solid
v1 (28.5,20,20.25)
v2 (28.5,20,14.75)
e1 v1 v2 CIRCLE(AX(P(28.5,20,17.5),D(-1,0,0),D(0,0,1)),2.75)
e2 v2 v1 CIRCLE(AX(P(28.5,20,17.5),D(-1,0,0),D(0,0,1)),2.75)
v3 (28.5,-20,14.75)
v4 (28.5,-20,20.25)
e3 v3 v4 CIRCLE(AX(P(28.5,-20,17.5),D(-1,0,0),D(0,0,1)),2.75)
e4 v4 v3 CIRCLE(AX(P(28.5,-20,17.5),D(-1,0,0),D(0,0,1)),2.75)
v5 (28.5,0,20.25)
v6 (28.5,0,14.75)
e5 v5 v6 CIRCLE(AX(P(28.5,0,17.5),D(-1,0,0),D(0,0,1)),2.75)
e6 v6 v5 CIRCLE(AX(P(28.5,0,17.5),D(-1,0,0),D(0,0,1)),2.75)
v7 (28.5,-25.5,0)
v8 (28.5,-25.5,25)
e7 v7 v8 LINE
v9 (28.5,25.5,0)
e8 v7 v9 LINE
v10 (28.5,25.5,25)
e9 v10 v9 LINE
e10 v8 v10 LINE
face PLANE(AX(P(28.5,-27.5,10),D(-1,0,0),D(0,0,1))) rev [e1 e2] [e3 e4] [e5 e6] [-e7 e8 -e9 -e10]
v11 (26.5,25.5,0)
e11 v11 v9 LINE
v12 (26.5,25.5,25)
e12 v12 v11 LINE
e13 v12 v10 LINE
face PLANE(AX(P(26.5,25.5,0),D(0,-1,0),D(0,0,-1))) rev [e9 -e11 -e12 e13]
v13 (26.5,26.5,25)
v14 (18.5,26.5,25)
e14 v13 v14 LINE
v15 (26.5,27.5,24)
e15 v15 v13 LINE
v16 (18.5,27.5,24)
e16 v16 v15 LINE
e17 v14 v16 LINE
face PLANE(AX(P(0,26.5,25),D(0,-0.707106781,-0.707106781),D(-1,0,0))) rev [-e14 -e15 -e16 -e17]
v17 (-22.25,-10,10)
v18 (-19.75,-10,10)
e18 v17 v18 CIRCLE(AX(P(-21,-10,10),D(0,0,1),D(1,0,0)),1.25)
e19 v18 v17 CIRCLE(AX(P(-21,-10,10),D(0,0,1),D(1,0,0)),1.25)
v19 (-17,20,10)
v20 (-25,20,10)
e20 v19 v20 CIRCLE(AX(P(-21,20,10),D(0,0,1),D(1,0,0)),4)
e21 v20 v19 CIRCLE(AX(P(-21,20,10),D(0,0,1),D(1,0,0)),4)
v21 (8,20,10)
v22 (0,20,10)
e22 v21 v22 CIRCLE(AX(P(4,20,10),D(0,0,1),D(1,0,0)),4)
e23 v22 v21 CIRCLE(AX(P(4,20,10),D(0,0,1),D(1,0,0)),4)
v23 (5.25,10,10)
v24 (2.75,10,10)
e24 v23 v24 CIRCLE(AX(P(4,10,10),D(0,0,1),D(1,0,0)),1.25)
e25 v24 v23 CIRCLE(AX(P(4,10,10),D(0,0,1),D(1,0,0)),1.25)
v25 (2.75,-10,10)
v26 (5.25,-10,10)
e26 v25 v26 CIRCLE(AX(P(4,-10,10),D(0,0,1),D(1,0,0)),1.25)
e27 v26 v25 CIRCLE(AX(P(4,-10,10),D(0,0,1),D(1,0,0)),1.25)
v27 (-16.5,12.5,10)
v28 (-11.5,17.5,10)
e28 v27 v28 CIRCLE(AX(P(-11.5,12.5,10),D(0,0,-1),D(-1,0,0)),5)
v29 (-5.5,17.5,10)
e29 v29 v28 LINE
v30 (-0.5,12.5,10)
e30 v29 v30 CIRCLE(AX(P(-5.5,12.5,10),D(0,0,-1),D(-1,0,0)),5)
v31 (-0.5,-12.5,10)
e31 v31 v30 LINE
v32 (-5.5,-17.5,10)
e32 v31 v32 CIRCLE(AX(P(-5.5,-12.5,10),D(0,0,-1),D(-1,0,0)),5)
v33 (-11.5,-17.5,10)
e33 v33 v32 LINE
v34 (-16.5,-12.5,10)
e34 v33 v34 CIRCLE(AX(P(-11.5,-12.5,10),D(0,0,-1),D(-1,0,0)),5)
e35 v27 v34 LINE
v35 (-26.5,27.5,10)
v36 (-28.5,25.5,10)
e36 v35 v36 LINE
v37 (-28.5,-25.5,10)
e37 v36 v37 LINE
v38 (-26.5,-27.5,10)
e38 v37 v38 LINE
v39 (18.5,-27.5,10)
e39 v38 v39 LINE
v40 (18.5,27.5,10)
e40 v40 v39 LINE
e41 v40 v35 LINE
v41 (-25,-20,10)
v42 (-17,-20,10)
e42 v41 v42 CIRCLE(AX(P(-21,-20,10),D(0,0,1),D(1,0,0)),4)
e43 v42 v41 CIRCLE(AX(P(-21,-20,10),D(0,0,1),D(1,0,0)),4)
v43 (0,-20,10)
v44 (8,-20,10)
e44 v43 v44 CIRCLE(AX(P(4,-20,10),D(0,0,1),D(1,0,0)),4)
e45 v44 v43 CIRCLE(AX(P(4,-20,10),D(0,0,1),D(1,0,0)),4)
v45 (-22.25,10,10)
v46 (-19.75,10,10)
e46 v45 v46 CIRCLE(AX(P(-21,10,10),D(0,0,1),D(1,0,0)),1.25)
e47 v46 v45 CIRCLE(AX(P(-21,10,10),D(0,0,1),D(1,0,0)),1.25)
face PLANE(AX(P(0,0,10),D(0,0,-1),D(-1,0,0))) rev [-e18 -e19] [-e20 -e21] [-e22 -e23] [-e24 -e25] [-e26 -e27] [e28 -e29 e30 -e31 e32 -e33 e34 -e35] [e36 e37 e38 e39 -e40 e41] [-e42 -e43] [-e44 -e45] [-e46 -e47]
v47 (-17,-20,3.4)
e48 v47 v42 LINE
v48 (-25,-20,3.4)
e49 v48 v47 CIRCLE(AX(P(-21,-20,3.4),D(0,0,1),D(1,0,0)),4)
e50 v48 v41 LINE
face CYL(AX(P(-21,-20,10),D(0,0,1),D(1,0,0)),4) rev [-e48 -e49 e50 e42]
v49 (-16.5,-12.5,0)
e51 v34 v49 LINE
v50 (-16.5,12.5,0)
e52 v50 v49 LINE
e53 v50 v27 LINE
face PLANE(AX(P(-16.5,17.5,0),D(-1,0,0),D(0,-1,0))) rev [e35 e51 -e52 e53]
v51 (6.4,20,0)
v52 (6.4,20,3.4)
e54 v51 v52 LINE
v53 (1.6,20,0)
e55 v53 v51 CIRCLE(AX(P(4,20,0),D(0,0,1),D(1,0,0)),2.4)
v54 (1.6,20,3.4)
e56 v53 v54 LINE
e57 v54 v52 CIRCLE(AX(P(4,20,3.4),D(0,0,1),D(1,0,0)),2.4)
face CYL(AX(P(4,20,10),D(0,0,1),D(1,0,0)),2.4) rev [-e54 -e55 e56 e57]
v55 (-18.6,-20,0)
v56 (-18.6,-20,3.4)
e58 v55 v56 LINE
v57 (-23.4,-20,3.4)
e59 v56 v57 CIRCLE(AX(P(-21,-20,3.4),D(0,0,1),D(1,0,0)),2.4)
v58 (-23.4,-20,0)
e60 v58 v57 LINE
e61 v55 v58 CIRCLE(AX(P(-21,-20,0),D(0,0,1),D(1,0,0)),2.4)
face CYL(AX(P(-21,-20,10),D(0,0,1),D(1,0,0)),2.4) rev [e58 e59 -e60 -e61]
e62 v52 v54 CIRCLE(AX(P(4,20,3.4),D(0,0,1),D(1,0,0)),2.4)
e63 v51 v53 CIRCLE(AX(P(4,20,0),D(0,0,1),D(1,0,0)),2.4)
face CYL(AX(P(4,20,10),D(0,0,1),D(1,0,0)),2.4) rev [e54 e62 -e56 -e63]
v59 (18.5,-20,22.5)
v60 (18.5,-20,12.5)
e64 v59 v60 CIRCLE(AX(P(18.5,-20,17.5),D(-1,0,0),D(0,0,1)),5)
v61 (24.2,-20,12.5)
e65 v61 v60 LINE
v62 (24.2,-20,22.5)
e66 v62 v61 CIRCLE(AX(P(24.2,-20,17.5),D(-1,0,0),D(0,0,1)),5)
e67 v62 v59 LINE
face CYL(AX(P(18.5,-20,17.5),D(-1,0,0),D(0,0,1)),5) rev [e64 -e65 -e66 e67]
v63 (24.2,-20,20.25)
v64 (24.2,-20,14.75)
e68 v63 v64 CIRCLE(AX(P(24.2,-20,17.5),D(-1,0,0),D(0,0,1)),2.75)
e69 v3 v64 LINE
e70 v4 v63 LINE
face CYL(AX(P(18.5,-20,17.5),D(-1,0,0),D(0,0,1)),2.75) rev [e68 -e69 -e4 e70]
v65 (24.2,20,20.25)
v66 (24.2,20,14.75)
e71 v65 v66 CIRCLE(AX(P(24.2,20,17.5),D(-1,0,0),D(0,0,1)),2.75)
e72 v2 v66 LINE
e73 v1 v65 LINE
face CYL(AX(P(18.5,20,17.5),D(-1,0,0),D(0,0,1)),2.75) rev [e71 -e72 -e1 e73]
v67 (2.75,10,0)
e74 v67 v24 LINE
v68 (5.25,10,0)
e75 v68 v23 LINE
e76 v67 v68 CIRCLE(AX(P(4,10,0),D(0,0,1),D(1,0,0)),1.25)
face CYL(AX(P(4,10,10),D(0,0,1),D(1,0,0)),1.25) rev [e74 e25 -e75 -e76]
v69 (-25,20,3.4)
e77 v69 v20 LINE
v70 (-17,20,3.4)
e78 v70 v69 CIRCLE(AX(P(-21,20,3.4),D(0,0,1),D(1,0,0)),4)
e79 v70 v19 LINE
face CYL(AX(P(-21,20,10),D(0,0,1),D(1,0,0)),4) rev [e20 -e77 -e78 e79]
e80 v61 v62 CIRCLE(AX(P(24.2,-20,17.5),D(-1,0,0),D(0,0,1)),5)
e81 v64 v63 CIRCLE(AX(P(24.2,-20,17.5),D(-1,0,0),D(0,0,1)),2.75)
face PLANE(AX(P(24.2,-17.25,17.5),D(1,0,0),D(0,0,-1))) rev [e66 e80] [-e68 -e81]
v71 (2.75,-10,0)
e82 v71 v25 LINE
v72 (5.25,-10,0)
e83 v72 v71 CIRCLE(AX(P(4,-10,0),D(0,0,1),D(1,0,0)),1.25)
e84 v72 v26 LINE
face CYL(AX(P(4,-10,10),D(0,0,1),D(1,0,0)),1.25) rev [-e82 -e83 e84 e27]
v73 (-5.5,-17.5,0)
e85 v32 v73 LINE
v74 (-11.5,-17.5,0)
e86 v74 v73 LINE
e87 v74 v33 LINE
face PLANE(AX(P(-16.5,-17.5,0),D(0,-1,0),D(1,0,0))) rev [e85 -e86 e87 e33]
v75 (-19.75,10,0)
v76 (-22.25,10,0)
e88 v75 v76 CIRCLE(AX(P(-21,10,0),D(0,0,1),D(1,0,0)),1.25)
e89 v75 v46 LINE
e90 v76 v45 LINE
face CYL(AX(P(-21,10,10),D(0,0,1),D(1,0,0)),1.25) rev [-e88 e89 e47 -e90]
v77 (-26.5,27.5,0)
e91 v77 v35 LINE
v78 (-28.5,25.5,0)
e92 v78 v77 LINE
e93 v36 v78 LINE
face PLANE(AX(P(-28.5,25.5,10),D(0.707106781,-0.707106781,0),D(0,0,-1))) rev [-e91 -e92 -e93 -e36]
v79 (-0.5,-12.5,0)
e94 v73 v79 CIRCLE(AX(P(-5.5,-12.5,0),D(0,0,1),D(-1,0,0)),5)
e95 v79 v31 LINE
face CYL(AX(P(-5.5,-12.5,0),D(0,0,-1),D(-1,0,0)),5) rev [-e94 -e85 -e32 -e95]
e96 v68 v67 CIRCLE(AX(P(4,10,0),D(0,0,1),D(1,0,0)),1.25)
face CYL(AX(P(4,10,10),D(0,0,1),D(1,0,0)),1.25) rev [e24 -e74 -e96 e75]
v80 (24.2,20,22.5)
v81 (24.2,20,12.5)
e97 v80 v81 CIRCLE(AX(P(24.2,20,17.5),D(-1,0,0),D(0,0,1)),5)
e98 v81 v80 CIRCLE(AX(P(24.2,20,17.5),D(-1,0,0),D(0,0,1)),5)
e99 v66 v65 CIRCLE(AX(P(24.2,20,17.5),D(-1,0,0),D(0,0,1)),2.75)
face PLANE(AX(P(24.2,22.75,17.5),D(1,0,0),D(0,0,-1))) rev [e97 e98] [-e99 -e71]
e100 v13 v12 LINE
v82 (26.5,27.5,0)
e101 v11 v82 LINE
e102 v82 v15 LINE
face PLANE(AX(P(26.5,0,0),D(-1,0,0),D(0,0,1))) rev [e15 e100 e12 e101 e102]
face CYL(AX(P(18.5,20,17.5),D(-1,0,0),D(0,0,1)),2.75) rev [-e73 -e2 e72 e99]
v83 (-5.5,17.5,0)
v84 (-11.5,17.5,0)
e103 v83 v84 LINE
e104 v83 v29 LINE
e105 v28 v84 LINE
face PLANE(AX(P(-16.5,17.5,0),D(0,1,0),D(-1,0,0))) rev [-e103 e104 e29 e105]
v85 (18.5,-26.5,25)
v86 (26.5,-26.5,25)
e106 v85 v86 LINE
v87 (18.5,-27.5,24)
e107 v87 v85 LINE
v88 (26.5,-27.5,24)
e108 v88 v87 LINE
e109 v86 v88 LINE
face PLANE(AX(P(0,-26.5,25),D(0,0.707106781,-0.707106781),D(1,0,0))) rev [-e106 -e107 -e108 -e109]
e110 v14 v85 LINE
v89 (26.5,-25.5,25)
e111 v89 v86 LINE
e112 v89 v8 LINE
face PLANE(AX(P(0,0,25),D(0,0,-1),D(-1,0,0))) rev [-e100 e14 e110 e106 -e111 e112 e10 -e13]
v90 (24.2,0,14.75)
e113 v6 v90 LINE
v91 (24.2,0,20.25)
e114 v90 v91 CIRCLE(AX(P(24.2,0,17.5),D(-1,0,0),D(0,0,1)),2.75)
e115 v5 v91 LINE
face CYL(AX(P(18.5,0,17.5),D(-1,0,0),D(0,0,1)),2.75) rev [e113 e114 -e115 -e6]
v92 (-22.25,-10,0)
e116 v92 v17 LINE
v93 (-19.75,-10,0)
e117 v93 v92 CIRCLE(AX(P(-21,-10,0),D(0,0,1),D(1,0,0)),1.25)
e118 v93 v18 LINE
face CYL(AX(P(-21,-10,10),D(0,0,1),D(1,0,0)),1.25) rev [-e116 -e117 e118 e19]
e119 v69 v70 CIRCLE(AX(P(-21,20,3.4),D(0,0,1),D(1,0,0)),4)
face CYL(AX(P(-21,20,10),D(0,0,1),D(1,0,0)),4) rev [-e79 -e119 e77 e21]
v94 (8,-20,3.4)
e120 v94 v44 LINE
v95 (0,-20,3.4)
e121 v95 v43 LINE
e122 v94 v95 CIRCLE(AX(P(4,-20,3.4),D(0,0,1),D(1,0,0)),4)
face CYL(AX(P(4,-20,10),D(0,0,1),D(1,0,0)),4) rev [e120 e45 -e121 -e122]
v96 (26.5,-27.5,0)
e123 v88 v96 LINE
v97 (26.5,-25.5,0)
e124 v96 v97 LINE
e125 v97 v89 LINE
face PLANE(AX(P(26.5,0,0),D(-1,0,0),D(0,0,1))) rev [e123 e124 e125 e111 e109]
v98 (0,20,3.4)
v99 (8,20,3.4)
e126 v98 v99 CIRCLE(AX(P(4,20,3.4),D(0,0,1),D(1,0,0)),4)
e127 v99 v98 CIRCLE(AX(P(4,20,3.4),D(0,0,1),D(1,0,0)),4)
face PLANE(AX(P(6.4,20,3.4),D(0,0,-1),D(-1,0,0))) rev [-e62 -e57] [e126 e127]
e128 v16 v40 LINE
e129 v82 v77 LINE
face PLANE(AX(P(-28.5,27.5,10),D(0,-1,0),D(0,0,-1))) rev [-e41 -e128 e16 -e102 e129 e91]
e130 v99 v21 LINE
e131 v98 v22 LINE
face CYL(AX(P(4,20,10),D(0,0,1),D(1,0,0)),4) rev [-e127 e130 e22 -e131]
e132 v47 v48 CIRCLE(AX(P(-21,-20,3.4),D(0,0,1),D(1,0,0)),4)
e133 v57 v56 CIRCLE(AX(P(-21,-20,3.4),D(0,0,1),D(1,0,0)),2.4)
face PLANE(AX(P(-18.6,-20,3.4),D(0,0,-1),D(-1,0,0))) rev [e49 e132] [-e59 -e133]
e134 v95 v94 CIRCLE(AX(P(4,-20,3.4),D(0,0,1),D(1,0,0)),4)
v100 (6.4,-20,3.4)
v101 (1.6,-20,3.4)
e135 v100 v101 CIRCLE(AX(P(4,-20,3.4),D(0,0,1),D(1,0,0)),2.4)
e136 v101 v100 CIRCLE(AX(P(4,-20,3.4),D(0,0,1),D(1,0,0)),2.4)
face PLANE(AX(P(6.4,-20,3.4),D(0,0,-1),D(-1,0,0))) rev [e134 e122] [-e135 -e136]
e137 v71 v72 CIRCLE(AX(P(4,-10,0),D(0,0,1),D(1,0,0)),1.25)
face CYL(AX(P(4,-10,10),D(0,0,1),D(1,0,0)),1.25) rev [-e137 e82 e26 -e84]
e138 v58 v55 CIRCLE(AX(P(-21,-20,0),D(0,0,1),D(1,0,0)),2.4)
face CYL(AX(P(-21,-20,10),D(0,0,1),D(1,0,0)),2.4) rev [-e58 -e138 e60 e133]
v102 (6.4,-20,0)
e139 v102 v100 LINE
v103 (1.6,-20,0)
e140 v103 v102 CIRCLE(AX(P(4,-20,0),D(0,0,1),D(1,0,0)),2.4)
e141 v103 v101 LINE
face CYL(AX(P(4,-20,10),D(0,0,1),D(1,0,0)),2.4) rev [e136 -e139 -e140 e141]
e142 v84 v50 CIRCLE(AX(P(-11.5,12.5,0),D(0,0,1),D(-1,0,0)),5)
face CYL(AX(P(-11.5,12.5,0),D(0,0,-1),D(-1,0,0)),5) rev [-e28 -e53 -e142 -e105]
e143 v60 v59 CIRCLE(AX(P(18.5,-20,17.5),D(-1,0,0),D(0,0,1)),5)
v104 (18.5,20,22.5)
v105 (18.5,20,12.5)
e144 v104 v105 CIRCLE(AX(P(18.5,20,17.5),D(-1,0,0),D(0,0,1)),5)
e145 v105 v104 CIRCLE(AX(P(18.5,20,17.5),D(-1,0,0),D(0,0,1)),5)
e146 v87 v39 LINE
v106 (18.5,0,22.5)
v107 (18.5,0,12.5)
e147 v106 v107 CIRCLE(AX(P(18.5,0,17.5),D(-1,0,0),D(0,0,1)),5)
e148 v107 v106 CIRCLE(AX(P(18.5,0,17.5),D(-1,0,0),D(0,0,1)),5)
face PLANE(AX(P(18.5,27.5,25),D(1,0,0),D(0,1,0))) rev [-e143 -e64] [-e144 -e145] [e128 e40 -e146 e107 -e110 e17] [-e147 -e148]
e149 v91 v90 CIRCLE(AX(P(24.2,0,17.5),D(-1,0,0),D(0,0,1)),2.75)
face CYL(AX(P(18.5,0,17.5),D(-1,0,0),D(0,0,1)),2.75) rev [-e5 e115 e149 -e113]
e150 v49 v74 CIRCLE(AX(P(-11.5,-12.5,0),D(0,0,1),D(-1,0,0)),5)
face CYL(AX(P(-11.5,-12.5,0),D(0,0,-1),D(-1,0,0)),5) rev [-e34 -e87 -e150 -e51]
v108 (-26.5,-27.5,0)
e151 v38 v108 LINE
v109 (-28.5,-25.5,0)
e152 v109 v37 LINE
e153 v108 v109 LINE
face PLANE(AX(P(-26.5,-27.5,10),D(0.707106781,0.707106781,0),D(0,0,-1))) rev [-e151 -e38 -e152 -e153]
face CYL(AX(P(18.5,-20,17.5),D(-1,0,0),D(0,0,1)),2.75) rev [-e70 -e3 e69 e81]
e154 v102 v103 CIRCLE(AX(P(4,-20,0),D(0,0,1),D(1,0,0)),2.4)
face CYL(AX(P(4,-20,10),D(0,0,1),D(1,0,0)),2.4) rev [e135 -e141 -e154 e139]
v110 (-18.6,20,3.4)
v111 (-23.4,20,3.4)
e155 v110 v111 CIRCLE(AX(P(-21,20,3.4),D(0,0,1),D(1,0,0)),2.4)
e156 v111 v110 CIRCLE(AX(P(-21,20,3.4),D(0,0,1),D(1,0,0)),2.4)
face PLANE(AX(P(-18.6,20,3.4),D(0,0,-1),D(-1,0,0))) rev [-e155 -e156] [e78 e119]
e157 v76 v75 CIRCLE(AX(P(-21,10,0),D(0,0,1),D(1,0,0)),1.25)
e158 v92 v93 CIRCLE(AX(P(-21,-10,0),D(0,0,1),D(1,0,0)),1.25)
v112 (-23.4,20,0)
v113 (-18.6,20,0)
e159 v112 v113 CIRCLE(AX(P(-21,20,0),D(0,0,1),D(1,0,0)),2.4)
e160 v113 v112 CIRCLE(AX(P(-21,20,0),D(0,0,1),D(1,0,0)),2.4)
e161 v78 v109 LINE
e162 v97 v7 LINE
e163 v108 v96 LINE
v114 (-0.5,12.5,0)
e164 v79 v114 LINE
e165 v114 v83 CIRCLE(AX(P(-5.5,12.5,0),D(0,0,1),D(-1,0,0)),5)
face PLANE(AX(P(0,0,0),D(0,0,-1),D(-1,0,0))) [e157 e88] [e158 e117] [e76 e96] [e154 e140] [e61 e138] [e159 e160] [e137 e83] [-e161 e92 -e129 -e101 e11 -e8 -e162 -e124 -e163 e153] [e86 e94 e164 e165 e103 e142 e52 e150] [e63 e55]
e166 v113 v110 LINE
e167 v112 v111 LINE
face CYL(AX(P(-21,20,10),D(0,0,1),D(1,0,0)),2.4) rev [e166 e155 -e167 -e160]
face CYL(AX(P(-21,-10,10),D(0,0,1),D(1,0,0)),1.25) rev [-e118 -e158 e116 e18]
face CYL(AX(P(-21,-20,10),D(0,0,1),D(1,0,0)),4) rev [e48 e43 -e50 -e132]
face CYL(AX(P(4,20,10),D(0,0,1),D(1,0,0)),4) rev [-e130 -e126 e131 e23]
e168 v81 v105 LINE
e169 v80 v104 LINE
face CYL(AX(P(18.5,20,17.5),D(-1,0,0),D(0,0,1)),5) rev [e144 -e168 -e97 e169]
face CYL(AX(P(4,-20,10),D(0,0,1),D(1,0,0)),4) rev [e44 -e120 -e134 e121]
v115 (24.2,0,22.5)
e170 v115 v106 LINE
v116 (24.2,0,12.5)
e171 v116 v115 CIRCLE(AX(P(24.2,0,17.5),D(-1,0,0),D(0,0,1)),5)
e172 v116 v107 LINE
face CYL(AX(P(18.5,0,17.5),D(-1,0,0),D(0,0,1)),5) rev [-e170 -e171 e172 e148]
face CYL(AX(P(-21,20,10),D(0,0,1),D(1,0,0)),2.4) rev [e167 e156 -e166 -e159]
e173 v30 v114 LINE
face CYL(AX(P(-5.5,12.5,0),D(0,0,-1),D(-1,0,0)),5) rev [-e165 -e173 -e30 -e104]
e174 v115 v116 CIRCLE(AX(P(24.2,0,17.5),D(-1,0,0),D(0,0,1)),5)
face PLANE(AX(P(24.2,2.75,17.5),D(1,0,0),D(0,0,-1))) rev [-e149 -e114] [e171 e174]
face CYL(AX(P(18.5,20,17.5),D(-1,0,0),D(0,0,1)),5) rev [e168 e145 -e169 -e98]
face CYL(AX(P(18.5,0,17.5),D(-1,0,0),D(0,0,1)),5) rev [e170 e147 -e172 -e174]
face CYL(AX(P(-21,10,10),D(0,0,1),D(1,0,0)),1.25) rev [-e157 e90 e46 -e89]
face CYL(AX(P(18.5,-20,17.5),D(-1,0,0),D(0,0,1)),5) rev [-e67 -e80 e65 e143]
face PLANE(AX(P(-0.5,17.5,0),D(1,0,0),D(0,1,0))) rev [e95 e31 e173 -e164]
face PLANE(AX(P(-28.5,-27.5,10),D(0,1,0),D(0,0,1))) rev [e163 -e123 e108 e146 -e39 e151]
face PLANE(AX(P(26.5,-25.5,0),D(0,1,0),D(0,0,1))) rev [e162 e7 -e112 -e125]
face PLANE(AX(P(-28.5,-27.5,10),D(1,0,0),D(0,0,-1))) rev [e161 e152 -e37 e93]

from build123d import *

# Parameters (mm, degrees)
SKETCH_1_W                = 57
SKETCH_1_H                = 55
EXTRUDE_1_DEPTH           = 10
SKETCH_2_W                = 16
SKETCH_2_H                = 35
CUT_EXTRUDE_1_DEPTH       = 41.847276531
HOLE_WIZARD_1_D           = 4.8
HOLE_WIZARD_1_CBORE_D     = 8
HOLE_WIZARD_1_CBORE_DEPTH = 6.6
HOLE_WIZARD_M3_1_D        = 2.5
FILLET_1_R                = 5
SKETCH_8_W                = 10
SKETCH_8_H                = 55
EXTRUDE_2_DEPTH           = 15
HOLE_WIZARD_2_D           = 5.5
HOLE_WIZARD_2_CBORE_D     = 10
HOLE_WIZARD_2_CBORE_DEPTH = 5.7
SKETCH_11_W               = 25
SKETCH_11_H               = 2
CUT_EXTRUDE_2_DEPTH       = 2
CHAMFER_3_SIZE            = 2
CHAMFER_4_SIZE            = 1


with BuildPart() as part:
    # 草图1 → 凸台-拉伸1 (new body)
    with BuildSketch(Plane.XY):
        Rectangle(SKETCH_1_W, SKETCH_1_H)
    extrude(amount=EXTRUDE_1_DEPTH)

    # 草图2 → 切除-拉伸1 (cut, through all)
    with BuildSketch(Plane.XY.offset(10)):
        with Locations((-8.5, 0)):
            Rectangle(SKETCH_2_W, SKETCH_2_H)
    extrude(amount=-CUT_EXTRUDE_1_DEPTH, mode=Mode.SUBTRACT)

    # 打孔尺寸(%根据)内六角圆柱头螺钉的类型1 (through all)
    with Locations(Plane.XY.offset(10)):
        with Locations((-21, 20), (4, 20), (-21, -20), (4, -20)):
            CounterBoreHole(HOLE_WIZARD_1_D / 2, HOLE_WIZARD_1_CBORE_D / 2, HOLE_WIZARD_1_CBORE_DEPTH)

    # M3 螺纹孔1 (through all)
    with Locations(Plane.XY.offset(10)):
        with Locations((-21, 10), (-21, -10), (4, 10), (4, -10)):
            Hole(HOLE_WIZARD_M3_1_D / 2)

    # 圆角1
    fillet_1_edges = [part.edges().sort_by_distance(p)[0] for p in [
        (-16.5, -17.5, 5),
        (-16.5, 17.5, 5),
        (-0.5, 17.5, 5),
        (-0.5, -17.5, 5),
    ]]
    fillet(fillet_1_edges, radius=FILLET_1_R)

    # 草图8 → 凸台-拉伸2 (add)
    with BuildSketch(Plane.XY.offset(10)):
        with Locations((23.5, 0)):
            Rectangle(SKETCH_8_W, SKETCH_8_H)
    extrude(amount=EXTRUDE_2_DEPTH)

    # 打孔尺寸(%根据)内六角圆柱头螺钉的类型2 (through all)
    with Locations(Plane.ZY.offset(-18.5)):
        with Locations((17.5, 20), (17.5, 0), (17.5, -20)):
            CounterBoreHole(HOLE_WIZARD_2_D / 2, HOLE_WIZARD_2_CBORE_D / 2, HOLE_WIZARD_2_CBORE_DEPTH)

    # 草图11 → 切除-拉伸2 (cut)
    with BuildSketch(Plane(origin=(28.5, 0, 0), x_dir=(0, 0, -1), z_dir=(1, 0, 0))):
        with Locations((-12.5, 26.5)):
            Rectangle(SKETCH_11_W, SKETCH_11_H)
        with Locations((-12.5, -26.5)):
            Rectangle(SKETCH_11_W, SKETCH_11_H)
    extrude(amount=-CUT_EXTRUDE_2_DEPTH, mode=Mode.SUBTRACT)

    # 倒角3
    chamfer_3_edges = [part.edges().sort_by_distance(p)[0] for p in [
        (-28.5, -27.5, 5),
        (-28.5, 27.5, 5),
    ]]
    chamfer(chamfer_3_edges, length=CHAMFER_3_SIZE)

    # 倒角4
    chamfer_4_edges = [part.edges().sort_by_distance(p)[0] for p in [
        (22.5, -27.5, 25),
        (22.5, 27.5, 25),
    ]]
    chamfer(chamfer_4_edges, length=CHAMFER_4_SIZE)


solid = part.part
